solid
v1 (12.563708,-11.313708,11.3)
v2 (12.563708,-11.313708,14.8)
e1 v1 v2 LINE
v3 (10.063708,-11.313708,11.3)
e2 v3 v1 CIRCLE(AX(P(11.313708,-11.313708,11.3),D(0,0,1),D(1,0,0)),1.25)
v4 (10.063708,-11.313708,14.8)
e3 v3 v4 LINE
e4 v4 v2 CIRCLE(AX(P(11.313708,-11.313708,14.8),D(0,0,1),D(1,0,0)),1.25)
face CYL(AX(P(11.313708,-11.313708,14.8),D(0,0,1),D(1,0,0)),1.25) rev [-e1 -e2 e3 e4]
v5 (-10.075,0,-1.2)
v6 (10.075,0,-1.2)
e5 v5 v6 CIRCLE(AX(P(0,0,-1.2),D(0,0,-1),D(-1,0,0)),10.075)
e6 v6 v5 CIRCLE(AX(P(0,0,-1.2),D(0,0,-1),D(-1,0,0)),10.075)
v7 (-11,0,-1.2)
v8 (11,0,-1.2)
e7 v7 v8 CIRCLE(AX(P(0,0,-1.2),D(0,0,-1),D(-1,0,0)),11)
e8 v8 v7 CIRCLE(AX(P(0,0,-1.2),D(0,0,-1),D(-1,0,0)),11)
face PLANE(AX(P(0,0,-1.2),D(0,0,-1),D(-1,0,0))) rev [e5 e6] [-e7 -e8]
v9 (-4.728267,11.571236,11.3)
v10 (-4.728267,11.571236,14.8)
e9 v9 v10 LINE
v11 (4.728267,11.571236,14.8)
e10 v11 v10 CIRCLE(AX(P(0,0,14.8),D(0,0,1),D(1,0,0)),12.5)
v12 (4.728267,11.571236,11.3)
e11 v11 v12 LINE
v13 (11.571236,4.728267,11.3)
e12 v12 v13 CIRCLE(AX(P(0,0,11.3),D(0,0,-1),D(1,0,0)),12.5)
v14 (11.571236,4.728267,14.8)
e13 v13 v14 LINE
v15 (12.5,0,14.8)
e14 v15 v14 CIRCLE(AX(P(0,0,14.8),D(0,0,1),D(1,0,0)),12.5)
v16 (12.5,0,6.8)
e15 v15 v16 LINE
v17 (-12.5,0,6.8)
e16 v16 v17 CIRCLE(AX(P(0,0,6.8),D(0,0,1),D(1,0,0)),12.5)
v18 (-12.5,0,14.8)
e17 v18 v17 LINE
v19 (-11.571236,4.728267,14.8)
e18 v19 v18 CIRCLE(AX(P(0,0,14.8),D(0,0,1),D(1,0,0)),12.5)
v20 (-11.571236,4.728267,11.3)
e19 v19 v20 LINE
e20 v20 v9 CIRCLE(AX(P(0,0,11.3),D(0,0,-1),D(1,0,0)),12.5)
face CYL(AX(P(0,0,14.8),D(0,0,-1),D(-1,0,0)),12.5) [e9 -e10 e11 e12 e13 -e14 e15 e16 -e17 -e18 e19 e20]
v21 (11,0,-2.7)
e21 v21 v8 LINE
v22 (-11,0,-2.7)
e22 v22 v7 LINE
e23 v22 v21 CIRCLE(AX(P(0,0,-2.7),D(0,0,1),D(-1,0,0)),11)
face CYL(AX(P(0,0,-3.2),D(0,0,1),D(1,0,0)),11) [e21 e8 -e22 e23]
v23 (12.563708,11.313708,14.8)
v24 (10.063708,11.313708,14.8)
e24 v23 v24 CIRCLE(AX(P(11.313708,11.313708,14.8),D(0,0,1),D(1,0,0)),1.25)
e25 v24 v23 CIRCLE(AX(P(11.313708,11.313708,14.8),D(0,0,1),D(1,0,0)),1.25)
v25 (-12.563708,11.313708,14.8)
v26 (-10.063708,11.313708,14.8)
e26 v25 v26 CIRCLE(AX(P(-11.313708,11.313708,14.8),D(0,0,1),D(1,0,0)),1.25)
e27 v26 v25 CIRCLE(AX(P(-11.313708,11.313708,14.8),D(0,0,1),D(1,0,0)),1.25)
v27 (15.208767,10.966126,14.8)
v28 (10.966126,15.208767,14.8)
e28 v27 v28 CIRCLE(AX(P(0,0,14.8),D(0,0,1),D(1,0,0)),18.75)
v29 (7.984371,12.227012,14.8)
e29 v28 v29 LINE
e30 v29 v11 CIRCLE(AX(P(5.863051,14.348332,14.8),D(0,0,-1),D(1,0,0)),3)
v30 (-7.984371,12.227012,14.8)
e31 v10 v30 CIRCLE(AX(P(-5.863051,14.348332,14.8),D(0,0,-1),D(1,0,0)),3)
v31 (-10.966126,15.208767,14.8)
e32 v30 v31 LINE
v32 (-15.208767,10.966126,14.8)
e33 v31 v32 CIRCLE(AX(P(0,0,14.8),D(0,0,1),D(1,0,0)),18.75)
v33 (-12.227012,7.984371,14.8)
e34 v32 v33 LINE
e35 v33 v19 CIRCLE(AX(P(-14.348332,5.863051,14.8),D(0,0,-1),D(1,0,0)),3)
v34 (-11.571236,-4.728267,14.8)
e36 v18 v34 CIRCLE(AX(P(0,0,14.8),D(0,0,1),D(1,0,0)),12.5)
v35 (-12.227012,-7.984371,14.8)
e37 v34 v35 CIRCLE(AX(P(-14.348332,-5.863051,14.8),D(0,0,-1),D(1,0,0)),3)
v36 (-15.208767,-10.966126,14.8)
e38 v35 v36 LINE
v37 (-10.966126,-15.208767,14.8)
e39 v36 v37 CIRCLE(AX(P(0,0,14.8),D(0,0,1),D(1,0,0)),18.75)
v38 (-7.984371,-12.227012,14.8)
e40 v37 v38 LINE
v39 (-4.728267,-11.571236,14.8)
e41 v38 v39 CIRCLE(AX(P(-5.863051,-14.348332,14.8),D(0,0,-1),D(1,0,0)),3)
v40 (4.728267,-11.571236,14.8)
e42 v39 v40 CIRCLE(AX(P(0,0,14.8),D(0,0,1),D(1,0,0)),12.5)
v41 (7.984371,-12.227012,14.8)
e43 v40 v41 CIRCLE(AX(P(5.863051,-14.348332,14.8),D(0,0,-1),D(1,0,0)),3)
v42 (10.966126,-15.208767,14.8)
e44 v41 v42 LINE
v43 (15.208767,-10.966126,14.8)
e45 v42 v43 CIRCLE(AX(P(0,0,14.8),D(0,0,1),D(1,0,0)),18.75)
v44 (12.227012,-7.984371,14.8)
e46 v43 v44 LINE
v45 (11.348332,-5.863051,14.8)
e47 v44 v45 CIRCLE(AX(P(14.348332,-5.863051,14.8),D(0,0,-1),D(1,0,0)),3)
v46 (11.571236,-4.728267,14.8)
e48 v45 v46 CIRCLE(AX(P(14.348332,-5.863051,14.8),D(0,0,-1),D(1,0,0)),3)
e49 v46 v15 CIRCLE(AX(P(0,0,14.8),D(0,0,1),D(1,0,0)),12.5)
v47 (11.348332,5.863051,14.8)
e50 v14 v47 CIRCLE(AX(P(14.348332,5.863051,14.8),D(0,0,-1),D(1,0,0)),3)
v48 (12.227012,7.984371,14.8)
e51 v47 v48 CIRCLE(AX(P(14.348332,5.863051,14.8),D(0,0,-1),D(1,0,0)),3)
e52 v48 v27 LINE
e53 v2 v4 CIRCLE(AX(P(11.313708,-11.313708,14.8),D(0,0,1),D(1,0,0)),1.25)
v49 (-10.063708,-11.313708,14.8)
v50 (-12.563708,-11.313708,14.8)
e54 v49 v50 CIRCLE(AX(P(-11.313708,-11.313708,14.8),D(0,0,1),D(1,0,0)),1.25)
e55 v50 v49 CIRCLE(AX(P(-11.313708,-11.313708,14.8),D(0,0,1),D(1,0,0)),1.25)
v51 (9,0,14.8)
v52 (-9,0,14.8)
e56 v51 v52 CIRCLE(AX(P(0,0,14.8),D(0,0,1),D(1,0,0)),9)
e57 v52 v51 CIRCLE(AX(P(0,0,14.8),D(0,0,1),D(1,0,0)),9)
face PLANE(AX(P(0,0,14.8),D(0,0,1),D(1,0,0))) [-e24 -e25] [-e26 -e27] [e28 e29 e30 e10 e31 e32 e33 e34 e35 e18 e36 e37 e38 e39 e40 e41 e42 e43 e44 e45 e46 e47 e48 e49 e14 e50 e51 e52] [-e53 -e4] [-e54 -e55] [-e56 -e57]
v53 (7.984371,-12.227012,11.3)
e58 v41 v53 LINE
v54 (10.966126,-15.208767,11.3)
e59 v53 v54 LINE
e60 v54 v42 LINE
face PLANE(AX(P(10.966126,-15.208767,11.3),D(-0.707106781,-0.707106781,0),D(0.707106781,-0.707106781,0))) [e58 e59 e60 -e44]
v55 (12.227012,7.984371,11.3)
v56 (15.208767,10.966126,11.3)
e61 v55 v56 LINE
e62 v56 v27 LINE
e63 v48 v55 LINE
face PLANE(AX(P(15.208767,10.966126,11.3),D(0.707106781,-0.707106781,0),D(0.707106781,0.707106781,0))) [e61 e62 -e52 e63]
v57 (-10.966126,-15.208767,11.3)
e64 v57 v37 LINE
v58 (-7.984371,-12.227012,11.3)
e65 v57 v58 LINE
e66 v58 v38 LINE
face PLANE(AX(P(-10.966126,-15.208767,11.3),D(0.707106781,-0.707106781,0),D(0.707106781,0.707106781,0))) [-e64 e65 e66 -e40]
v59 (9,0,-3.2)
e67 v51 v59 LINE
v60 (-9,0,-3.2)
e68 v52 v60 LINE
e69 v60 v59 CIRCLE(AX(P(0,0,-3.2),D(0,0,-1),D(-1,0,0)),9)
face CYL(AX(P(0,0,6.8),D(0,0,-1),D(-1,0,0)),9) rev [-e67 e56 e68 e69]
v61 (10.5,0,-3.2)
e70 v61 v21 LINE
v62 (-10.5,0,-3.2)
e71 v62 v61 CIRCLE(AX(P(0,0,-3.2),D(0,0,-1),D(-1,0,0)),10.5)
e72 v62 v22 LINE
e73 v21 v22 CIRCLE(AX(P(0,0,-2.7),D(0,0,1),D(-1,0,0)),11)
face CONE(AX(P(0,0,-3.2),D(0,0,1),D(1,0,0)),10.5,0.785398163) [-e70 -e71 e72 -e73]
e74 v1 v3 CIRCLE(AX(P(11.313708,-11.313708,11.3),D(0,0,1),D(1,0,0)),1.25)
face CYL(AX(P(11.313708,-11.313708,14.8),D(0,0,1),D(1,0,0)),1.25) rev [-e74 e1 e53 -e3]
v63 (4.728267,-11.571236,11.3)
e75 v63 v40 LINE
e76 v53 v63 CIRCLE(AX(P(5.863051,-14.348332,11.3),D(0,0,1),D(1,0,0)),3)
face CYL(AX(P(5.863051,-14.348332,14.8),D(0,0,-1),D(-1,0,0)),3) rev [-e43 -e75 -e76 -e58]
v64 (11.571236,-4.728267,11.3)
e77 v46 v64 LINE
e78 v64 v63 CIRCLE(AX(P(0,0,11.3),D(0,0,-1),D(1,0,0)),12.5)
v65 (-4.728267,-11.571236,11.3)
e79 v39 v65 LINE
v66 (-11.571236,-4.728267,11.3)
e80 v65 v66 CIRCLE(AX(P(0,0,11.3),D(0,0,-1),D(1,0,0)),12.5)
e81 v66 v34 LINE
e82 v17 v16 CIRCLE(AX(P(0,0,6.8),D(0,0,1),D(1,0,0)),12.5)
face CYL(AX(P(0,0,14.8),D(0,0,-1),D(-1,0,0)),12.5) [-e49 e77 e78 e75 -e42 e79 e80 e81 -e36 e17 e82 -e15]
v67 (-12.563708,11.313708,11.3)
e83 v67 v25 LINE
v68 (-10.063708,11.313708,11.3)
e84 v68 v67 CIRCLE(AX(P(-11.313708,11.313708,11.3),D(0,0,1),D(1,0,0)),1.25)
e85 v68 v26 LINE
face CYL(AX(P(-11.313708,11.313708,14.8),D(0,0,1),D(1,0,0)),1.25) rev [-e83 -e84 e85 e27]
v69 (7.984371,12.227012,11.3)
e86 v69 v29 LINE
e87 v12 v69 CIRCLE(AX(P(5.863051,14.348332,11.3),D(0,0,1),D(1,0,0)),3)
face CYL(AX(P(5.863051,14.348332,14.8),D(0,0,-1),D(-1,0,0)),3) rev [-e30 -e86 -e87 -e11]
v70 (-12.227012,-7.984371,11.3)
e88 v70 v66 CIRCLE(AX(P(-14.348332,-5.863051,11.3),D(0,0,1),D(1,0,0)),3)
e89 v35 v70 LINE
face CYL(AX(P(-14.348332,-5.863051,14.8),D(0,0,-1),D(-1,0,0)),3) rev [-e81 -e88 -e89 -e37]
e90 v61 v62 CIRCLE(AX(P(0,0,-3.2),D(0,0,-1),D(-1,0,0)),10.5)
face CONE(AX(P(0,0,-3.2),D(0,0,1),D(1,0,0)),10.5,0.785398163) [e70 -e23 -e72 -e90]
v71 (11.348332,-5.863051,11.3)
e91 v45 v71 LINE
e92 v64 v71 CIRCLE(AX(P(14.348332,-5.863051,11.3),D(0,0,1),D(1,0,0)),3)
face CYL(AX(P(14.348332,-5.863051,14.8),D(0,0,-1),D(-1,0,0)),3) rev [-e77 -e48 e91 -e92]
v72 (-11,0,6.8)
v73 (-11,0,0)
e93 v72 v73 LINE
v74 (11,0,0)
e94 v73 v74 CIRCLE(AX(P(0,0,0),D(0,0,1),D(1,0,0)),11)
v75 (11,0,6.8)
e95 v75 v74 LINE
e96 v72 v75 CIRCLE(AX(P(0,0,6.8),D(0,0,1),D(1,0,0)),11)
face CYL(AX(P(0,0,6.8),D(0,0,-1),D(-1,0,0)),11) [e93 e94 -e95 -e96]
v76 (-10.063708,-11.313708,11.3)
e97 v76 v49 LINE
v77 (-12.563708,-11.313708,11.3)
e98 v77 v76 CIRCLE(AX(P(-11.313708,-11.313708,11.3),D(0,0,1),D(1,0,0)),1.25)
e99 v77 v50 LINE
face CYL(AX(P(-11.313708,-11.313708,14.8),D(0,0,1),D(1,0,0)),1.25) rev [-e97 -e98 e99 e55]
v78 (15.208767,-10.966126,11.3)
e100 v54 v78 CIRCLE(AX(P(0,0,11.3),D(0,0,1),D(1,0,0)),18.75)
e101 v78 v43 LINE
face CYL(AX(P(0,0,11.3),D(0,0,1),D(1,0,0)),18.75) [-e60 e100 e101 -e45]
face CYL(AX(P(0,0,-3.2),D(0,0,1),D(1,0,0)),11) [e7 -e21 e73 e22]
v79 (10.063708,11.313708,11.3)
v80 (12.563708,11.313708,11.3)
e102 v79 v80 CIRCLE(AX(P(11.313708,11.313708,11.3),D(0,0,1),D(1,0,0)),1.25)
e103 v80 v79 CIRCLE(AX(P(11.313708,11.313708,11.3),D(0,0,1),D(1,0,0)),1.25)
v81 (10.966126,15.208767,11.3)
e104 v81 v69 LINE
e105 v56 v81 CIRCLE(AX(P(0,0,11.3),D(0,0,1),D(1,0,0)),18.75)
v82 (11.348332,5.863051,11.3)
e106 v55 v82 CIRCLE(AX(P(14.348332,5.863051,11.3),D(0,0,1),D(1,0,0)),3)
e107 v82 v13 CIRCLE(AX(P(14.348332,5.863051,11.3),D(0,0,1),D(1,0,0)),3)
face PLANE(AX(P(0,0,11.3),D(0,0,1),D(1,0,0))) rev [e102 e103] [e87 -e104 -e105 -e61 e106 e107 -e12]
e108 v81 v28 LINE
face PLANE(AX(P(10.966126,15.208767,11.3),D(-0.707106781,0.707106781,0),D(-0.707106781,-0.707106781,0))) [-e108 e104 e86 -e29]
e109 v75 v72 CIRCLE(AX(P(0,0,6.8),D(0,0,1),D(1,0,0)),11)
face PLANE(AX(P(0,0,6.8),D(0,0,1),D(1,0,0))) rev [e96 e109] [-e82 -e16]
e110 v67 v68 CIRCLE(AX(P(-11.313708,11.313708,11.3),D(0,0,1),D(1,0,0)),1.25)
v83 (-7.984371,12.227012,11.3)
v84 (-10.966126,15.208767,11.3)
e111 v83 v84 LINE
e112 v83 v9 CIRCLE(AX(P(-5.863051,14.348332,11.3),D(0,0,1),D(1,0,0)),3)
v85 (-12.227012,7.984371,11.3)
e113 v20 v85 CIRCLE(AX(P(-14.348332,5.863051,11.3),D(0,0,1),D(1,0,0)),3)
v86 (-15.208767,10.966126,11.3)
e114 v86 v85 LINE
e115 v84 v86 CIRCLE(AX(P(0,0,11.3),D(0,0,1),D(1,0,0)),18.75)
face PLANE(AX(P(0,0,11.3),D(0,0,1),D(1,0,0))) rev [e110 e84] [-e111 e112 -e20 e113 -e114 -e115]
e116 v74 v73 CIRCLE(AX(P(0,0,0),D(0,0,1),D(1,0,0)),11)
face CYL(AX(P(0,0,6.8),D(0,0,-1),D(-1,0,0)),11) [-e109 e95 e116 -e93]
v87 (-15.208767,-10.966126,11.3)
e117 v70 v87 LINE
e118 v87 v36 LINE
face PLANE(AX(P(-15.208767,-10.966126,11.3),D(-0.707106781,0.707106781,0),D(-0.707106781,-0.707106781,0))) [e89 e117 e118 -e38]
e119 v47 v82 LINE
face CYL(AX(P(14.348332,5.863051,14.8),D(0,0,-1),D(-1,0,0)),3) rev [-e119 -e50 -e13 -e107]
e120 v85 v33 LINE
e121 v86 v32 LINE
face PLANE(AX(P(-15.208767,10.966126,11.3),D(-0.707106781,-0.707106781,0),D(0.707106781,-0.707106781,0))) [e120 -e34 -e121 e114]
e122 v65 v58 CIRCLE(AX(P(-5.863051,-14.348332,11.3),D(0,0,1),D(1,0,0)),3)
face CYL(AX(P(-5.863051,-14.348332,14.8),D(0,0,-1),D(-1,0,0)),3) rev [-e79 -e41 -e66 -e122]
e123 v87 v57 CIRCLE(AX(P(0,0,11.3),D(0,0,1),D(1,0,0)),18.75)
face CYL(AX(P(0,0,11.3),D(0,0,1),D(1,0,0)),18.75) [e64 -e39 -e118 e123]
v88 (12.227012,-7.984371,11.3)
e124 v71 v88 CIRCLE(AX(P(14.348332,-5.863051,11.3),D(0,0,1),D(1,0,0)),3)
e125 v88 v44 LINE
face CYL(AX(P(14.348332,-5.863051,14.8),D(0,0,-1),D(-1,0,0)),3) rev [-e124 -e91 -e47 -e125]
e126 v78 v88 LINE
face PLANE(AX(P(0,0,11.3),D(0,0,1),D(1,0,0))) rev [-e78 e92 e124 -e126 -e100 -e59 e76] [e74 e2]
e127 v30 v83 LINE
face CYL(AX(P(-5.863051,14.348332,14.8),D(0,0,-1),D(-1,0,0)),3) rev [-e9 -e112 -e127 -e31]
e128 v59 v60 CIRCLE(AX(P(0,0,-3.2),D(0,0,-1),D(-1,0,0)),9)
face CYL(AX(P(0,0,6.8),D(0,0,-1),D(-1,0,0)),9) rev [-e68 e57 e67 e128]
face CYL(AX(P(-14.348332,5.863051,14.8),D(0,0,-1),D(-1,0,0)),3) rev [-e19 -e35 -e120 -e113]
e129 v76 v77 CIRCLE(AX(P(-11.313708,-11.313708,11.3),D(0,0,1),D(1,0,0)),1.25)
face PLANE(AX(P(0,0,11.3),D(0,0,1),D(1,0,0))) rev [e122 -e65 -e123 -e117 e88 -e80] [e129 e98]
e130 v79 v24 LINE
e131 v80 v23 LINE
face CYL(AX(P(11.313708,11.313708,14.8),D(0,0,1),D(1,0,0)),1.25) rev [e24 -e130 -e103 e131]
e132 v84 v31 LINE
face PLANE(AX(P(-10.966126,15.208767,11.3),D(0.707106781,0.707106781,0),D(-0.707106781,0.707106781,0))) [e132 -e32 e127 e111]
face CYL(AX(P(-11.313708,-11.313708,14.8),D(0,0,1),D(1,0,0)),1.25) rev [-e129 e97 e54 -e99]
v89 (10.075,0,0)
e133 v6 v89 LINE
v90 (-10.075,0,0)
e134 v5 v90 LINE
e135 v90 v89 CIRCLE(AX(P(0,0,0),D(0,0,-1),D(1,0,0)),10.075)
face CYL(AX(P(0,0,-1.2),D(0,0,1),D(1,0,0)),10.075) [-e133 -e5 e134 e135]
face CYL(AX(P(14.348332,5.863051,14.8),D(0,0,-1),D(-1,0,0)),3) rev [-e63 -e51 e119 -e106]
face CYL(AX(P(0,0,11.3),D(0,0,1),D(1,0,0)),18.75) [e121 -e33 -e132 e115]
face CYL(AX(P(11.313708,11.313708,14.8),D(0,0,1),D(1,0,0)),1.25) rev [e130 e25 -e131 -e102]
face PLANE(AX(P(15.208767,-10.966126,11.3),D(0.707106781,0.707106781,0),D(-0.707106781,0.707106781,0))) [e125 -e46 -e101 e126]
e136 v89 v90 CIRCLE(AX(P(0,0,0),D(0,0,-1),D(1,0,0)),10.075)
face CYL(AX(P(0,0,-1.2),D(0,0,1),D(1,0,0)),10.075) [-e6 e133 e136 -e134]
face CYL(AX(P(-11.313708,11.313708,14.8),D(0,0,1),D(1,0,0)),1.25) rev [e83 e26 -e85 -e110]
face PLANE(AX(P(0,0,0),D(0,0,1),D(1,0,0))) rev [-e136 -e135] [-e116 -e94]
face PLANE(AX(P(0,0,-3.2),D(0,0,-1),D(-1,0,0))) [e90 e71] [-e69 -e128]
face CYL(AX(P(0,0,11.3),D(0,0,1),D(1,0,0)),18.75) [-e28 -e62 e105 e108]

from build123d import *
from build123d.topology import SkipClean

# Parameters (mm, degrees)
SKETCH_1_R          = 11
SKETCH_1_R_2        = 9
EXTRUDE_1_DEPTH     = 6.8
SKETCH_2_R          = 12.5
SKETCH_2_R_2        = 9
EXTRUDE_2_DEPTH     = 8
SKETCH_4_R          = 12.5
SKETCH_4_R_2        = 9
EXTRUDE_3_DEPTH     = 5
CUT_EXTRUDE_START   = -5
SKETCH_8_R          = 12.5
SKETCH_8_R_2        = 9
CUT_EXTRUDE_1_DEPTH = 5
EXTRUDE_START       = -3.5
EXTRUDE_4_DEPTH     = 3.5
HOLE_WIZARD_M3_1_D  = 2.5
FILLET_1_R          = 3
EXTRUDE_START_2     = 1.2
SKETCH_13_R         = 10.075
SKETCH_13_R_2       = 9
EXTRUDE_5_DEPTH     = 1.2
EXTRUDE_START_3     = 2
SKETCH_14_R         = 11
SKETCH_14_R_2       = 9
EXTRUDE_6_DEPTH     = 2
CHAMFER_2_SIZE      = 0.5


with BuildPart() as part:
    # 草图1 → 凸台-拉伸1 (new body)
    with BuildSketch(Plane.XY):
        Circle(SKETCH_1_R)
        Circle(SKETCH_1_R_2, mode=Mode.SUBTRACT)
    extrude(amount=EXTRUDE_1_DEPTH)

    # 草图2 → 凸台-拉伸2 (add)
    with BuildSketch(Plane.XY.offset(6.8)):
        Circle(SKETCH_2_R)
        Circle(SKETCH_2_R_2, mode=Mode.SUBTRACT)
    extrude(amount=EXTRUDE_2_DEPTH)

    # 草图4 → 凸台-拉伸3 (add)
    with BuildSketch(Plane.XY.offset(14.8)):
        Circle(SKETCH_4_R)
        Circle(SKETCH_4_R_2, mode=Mode.SUBTRACT)
    extrude(amount=EXTRUDE_3_DEPTH)

    # 草图8 → 切除-拉伸1 (cut)
    with BuildSketch(Plane.XY.offset(19.8).offset(CUT_EXTRUDE_START)):
        Circle(SKETCH_8_R)
        Circle(SKETCH_8_R_2, mode=Mode.SUBTRACT)
    extrude(amount=CUT_EXTRUDE_1_DEPTH, mode=Mode.SUBTRACT)

    # 草图9 → 凸台-拉伸4 (add)
    with BuildSketch(Plane.XY.offset(14.8).offset(EXTRUDE_START)):
        with BuildLine():
            Line((10.966125931, 15.208766619), (6.459180807, 10.701821494))
            ThreePointArc((6.459180807, 10.701821494), (8.838834765, 8.838834765), (10.701821494, 6.459180807))
            Line((10.701821494, 6.459180807), (15.208766619, 10.966125931))
            ThreePointArc((15.208766619, 10.966125931), (13.258252147, 13.258252147), (10.966125931, 15.208766619))
        make_face()
        with BuildLine():
            Line((15.208766619, -10.966125931), (10.701821494, -6.459180807))
            ThreePointArc((10.701821494, -6.459180807), (8.838834765, -8.838834765), (6.459180807, -10.701821494))
            Line((6.459180807, -10.701821494), (10.966125931, -15.208766619))
            ThreePointArc((10.966125931, -15.208766619), (13.258252147, -13.258252147), (15.208766619, -10.966125931))
        make_face()
        with BuildLine():
            Line((-10.966125931, -15.208766619), (-6.459180807, -10.701821494))
            ThreePointArc((-6.459180807, -10.701821494), (-8.838834765, -8.838834765), (-10.701821494, -6.459180807))
            Line((-10.701821494, -6.459180807), (-15.208766619, -10.966125931))
            ThreePointArc((-15.208766619, -10.966125931), (-13.258252147, -13.258252147), (-10.966125931, -15.208766619))
        make_face()
        with BuildLine():
            Line((-15.208766619, 10.966125931), (-10.701821494, 6.459180807))
            ThreePointArc((-10.701821494, 6.459180807), (-8.838834765, 8.838834765), (-6.459180807, 10.701821494))
            Line((-6.459180807, 10.701821494), (-10.966125931, 15.208766619))
            ThreePointArc((-10.966125931, 15.208766619), (-13.258252147, 13.258252147), (-15.208766619, 10.966125931))
        make_face()
    extrude(amount=EXTRUDE_4_DEPTH)

    # M3 螺纹孔1 (through all)
    with Locations(Plane.XY.offset(14.8)):
        with Locations((-11.313708499, 11.313708499), (11.313708499, 11.313708499), (11.313708499, -11.313708499), (-11.313708499, -11.313708499)):
            Hole(HOLE_WIZARD_M3_1_D / 2)

    # 圆角1
    fillet_1_edges = [part.edges().sort_by_distance(p)[0] for p in [
        (10.701821494, 6.459180807, 13.05),
        (6.459180807, 10.701821494, 13.05),
        (6.459180807, -10.701821494, 13.05),
        (10.701821494, -6.459180807, 13.05),
        (-10.701821494, -6.459180807, 13.05),
        (-6.459180807, -10.701821494, 13.05),
        (-6.459180807, 10.701821494, 13.05),
        (-10.701821494, 6.459180807, 13.05),
    ]]
    fillet(fillet_1_edges, radius=FILLET_1_R)

    # 草图13 → 凸台-拉伸5 (add)
    with SkipClean():  # the faces are left unmerged after this step: merging them gives an invalid solid
        with BuildSketch(Plane(origin=(0, 0, 0), x_dir=(-1, 0, 0), z_dir=(0, 0, -1)).offset(EXTRUDE_START_2)):
            with Locations(Location((0, 0, 0), (0, 0, 180))):
                Circle(SKETCH_13_R)
            Circle(SKETCH_13_R_2, mode=Mode.SUBTRACT)
        extrude(amount=-EXTRUDE_5_DEPTH)

    # 草图14 → 凸台-拉伸6 (add)
    with SkipClean():  # the faces are left unmerged after this step: merging them gives an invalid solid
        with BuildSketch(Plane(origin=(0, 0, -1.2), x_dir=(-1, 0, 0), z_dir=(0, 0, -1)).offset(EXTRUDE_START_3)):
            with Locations(Location((0, 0, 0), (0, 0, 180))):
                Circle(SKETCH_14_R)
            Circle(SKETCH_14_R_2, mode=Mode.SUBTRACT)
        extrude(amount=-EXTRUDE_6_DEPTH)

    # 倒角2
    chamfer_2_edges = [part.edges().sort_by_distance(p)[0] for p in [
        (-11, 0, -3.2),
    ]]
    chamfer(chamfer_2_edges, length=CHAMFER_2_SIZE)


solid = part.part
